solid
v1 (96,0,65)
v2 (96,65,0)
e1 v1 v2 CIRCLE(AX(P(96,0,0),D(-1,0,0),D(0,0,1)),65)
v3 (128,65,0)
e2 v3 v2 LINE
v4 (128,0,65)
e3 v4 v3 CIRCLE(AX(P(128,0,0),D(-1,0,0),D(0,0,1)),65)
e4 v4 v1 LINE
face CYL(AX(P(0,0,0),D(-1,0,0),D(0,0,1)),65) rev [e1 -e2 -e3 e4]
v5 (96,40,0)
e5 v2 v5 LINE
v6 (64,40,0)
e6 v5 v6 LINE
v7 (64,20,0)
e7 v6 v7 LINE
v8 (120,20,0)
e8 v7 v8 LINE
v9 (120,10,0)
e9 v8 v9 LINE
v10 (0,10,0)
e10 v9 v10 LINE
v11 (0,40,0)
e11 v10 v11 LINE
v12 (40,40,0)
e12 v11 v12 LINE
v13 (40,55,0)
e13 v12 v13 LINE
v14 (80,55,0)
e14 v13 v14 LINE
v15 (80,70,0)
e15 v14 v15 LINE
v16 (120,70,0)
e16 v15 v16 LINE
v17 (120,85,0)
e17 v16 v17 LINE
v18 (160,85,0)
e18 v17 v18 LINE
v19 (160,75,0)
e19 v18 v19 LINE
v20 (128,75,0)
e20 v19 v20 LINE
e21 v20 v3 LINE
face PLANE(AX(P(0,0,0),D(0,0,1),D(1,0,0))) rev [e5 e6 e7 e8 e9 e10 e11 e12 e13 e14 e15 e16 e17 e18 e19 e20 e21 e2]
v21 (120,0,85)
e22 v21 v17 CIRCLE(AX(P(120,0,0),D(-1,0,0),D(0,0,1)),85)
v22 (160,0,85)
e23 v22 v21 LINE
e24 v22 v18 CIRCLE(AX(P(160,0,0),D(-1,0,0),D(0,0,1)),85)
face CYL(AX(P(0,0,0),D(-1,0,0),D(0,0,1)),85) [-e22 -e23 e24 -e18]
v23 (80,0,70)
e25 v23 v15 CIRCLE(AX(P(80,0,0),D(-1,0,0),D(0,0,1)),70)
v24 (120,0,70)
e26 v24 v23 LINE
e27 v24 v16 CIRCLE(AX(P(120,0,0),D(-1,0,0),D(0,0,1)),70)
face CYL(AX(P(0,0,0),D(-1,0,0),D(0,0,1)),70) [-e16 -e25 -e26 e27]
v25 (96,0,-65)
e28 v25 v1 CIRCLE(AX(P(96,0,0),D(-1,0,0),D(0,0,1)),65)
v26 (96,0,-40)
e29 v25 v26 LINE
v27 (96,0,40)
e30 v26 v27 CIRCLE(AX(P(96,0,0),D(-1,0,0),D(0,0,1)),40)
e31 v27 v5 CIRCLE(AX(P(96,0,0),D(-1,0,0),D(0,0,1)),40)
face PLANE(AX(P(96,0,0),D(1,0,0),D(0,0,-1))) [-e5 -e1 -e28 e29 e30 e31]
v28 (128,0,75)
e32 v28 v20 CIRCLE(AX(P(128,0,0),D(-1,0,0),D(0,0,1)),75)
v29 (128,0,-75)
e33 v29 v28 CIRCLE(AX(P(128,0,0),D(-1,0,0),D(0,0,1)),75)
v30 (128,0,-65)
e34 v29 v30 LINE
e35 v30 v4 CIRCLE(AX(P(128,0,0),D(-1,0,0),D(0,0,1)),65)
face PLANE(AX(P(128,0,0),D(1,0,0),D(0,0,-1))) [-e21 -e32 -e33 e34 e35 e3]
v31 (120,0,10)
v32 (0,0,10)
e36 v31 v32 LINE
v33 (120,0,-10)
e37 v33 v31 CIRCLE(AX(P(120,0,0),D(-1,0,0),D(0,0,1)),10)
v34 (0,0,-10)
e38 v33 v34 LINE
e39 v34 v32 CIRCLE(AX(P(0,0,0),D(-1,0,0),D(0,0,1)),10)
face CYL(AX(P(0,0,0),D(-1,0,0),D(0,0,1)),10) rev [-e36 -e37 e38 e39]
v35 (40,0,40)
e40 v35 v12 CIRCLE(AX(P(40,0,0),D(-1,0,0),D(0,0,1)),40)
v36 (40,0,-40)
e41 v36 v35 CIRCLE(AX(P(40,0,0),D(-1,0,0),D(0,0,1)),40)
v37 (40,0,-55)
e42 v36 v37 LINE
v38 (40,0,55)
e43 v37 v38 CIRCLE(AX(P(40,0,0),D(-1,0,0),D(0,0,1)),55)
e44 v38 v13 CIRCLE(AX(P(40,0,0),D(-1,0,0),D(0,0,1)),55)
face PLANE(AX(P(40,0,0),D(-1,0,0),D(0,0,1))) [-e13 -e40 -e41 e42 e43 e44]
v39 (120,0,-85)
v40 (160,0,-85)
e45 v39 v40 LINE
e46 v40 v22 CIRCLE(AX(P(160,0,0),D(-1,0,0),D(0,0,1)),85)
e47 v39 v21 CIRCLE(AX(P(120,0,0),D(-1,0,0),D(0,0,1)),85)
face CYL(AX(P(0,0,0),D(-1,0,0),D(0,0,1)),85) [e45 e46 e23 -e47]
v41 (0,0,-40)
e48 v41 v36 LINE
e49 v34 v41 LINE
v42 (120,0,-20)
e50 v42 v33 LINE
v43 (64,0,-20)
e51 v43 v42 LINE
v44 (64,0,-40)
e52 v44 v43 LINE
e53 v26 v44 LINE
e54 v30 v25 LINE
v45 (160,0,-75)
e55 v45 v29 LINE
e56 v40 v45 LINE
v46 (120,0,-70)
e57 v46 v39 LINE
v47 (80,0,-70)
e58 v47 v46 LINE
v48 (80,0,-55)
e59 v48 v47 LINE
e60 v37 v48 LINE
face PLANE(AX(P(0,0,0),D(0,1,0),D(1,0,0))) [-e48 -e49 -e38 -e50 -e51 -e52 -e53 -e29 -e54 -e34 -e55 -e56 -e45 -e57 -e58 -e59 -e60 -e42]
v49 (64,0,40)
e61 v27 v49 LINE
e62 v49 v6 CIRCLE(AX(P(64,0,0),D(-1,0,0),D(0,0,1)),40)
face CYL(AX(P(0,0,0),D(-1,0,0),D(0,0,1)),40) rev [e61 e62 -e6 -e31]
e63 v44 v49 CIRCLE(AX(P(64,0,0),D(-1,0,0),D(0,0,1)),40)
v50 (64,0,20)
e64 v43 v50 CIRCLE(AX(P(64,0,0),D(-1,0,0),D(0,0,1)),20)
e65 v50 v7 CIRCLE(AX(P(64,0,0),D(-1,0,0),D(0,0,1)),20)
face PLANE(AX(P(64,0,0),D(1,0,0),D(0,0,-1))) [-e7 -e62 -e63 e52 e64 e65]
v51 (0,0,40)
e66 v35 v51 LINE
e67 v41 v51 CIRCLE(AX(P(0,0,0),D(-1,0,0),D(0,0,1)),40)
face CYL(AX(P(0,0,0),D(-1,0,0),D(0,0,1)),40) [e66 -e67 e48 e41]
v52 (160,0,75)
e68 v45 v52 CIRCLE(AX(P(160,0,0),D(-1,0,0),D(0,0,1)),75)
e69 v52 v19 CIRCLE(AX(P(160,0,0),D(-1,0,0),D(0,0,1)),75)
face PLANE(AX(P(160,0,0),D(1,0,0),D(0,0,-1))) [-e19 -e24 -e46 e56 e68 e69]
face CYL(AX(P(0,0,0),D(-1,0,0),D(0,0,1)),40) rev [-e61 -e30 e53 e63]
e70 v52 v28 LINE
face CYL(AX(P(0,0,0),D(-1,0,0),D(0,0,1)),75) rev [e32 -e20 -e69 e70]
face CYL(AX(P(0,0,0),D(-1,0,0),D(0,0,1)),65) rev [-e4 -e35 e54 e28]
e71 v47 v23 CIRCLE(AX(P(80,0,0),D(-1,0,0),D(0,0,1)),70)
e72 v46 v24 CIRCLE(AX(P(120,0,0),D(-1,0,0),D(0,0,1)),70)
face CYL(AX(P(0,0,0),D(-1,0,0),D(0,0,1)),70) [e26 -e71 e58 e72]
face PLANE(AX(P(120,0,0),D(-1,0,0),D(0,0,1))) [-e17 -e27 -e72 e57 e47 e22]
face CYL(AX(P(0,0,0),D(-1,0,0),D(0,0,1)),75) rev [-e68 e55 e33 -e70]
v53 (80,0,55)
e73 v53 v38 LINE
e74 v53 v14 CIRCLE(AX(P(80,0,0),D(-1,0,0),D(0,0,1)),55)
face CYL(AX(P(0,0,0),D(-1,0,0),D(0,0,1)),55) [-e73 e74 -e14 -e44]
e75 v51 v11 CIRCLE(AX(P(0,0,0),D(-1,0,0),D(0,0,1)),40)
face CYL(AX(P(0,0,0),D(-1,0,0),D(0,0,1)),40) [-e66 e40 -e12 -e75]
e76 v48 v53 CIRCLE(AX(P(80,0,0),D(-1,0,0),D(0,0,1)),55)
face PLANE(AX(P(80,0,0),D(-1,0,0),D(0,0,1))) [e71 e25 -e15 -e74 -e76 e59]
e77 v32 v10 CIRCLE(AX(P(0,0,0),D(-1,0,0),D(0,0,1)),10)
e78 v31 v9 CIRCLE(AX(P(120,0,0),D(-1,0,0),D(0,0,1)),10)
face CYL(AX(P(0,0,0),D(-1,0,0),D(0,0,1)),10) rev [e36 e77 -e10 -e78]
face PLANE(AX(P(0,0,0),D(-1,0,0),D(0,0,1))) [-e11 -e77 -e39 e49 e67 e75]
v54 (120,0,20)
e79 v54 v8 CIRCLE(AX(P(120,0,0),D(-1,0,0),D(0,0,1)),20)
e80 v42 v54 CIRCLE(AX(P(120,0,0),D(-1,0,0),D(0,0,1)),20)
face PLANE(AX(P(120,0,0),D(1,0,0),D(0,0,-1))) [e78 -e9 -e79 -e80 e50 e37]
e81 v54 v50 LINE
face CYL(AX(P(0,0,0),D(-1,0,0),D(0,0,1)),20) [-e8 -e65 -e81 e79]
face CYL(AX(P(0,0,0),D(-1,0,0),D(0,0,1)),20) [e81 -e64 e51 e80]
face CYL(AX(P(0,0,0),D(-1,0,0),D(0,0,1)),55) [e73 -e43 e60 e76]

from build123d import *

# Parameters (mm, degrees)
HOUSING_REVOLVE_270DEG_ANGLE = 270


with BuildPart() as part:
    # Stepped Housing Profile → Housing Revolve 270deg (revolve)
    with BuildSketch(Plane.XY):
        Polygon((0, 40), (0, 10), (120, 10), (120, 20), (64, 20), (64, 40), (96, 40), (96, 65), (128, 65), (128, 75), (160, 75), (160, 85), (120, 85), (120, 70), (80, 70), (80, 55), (40, 55), (40, 40), align=None)
    revolve(axis=Axis((0, 0, 0), (1, 0, 0)), revolution_arc=HOUSING_REVOLVE_270DEG_ANGLE)


solid = part.part
